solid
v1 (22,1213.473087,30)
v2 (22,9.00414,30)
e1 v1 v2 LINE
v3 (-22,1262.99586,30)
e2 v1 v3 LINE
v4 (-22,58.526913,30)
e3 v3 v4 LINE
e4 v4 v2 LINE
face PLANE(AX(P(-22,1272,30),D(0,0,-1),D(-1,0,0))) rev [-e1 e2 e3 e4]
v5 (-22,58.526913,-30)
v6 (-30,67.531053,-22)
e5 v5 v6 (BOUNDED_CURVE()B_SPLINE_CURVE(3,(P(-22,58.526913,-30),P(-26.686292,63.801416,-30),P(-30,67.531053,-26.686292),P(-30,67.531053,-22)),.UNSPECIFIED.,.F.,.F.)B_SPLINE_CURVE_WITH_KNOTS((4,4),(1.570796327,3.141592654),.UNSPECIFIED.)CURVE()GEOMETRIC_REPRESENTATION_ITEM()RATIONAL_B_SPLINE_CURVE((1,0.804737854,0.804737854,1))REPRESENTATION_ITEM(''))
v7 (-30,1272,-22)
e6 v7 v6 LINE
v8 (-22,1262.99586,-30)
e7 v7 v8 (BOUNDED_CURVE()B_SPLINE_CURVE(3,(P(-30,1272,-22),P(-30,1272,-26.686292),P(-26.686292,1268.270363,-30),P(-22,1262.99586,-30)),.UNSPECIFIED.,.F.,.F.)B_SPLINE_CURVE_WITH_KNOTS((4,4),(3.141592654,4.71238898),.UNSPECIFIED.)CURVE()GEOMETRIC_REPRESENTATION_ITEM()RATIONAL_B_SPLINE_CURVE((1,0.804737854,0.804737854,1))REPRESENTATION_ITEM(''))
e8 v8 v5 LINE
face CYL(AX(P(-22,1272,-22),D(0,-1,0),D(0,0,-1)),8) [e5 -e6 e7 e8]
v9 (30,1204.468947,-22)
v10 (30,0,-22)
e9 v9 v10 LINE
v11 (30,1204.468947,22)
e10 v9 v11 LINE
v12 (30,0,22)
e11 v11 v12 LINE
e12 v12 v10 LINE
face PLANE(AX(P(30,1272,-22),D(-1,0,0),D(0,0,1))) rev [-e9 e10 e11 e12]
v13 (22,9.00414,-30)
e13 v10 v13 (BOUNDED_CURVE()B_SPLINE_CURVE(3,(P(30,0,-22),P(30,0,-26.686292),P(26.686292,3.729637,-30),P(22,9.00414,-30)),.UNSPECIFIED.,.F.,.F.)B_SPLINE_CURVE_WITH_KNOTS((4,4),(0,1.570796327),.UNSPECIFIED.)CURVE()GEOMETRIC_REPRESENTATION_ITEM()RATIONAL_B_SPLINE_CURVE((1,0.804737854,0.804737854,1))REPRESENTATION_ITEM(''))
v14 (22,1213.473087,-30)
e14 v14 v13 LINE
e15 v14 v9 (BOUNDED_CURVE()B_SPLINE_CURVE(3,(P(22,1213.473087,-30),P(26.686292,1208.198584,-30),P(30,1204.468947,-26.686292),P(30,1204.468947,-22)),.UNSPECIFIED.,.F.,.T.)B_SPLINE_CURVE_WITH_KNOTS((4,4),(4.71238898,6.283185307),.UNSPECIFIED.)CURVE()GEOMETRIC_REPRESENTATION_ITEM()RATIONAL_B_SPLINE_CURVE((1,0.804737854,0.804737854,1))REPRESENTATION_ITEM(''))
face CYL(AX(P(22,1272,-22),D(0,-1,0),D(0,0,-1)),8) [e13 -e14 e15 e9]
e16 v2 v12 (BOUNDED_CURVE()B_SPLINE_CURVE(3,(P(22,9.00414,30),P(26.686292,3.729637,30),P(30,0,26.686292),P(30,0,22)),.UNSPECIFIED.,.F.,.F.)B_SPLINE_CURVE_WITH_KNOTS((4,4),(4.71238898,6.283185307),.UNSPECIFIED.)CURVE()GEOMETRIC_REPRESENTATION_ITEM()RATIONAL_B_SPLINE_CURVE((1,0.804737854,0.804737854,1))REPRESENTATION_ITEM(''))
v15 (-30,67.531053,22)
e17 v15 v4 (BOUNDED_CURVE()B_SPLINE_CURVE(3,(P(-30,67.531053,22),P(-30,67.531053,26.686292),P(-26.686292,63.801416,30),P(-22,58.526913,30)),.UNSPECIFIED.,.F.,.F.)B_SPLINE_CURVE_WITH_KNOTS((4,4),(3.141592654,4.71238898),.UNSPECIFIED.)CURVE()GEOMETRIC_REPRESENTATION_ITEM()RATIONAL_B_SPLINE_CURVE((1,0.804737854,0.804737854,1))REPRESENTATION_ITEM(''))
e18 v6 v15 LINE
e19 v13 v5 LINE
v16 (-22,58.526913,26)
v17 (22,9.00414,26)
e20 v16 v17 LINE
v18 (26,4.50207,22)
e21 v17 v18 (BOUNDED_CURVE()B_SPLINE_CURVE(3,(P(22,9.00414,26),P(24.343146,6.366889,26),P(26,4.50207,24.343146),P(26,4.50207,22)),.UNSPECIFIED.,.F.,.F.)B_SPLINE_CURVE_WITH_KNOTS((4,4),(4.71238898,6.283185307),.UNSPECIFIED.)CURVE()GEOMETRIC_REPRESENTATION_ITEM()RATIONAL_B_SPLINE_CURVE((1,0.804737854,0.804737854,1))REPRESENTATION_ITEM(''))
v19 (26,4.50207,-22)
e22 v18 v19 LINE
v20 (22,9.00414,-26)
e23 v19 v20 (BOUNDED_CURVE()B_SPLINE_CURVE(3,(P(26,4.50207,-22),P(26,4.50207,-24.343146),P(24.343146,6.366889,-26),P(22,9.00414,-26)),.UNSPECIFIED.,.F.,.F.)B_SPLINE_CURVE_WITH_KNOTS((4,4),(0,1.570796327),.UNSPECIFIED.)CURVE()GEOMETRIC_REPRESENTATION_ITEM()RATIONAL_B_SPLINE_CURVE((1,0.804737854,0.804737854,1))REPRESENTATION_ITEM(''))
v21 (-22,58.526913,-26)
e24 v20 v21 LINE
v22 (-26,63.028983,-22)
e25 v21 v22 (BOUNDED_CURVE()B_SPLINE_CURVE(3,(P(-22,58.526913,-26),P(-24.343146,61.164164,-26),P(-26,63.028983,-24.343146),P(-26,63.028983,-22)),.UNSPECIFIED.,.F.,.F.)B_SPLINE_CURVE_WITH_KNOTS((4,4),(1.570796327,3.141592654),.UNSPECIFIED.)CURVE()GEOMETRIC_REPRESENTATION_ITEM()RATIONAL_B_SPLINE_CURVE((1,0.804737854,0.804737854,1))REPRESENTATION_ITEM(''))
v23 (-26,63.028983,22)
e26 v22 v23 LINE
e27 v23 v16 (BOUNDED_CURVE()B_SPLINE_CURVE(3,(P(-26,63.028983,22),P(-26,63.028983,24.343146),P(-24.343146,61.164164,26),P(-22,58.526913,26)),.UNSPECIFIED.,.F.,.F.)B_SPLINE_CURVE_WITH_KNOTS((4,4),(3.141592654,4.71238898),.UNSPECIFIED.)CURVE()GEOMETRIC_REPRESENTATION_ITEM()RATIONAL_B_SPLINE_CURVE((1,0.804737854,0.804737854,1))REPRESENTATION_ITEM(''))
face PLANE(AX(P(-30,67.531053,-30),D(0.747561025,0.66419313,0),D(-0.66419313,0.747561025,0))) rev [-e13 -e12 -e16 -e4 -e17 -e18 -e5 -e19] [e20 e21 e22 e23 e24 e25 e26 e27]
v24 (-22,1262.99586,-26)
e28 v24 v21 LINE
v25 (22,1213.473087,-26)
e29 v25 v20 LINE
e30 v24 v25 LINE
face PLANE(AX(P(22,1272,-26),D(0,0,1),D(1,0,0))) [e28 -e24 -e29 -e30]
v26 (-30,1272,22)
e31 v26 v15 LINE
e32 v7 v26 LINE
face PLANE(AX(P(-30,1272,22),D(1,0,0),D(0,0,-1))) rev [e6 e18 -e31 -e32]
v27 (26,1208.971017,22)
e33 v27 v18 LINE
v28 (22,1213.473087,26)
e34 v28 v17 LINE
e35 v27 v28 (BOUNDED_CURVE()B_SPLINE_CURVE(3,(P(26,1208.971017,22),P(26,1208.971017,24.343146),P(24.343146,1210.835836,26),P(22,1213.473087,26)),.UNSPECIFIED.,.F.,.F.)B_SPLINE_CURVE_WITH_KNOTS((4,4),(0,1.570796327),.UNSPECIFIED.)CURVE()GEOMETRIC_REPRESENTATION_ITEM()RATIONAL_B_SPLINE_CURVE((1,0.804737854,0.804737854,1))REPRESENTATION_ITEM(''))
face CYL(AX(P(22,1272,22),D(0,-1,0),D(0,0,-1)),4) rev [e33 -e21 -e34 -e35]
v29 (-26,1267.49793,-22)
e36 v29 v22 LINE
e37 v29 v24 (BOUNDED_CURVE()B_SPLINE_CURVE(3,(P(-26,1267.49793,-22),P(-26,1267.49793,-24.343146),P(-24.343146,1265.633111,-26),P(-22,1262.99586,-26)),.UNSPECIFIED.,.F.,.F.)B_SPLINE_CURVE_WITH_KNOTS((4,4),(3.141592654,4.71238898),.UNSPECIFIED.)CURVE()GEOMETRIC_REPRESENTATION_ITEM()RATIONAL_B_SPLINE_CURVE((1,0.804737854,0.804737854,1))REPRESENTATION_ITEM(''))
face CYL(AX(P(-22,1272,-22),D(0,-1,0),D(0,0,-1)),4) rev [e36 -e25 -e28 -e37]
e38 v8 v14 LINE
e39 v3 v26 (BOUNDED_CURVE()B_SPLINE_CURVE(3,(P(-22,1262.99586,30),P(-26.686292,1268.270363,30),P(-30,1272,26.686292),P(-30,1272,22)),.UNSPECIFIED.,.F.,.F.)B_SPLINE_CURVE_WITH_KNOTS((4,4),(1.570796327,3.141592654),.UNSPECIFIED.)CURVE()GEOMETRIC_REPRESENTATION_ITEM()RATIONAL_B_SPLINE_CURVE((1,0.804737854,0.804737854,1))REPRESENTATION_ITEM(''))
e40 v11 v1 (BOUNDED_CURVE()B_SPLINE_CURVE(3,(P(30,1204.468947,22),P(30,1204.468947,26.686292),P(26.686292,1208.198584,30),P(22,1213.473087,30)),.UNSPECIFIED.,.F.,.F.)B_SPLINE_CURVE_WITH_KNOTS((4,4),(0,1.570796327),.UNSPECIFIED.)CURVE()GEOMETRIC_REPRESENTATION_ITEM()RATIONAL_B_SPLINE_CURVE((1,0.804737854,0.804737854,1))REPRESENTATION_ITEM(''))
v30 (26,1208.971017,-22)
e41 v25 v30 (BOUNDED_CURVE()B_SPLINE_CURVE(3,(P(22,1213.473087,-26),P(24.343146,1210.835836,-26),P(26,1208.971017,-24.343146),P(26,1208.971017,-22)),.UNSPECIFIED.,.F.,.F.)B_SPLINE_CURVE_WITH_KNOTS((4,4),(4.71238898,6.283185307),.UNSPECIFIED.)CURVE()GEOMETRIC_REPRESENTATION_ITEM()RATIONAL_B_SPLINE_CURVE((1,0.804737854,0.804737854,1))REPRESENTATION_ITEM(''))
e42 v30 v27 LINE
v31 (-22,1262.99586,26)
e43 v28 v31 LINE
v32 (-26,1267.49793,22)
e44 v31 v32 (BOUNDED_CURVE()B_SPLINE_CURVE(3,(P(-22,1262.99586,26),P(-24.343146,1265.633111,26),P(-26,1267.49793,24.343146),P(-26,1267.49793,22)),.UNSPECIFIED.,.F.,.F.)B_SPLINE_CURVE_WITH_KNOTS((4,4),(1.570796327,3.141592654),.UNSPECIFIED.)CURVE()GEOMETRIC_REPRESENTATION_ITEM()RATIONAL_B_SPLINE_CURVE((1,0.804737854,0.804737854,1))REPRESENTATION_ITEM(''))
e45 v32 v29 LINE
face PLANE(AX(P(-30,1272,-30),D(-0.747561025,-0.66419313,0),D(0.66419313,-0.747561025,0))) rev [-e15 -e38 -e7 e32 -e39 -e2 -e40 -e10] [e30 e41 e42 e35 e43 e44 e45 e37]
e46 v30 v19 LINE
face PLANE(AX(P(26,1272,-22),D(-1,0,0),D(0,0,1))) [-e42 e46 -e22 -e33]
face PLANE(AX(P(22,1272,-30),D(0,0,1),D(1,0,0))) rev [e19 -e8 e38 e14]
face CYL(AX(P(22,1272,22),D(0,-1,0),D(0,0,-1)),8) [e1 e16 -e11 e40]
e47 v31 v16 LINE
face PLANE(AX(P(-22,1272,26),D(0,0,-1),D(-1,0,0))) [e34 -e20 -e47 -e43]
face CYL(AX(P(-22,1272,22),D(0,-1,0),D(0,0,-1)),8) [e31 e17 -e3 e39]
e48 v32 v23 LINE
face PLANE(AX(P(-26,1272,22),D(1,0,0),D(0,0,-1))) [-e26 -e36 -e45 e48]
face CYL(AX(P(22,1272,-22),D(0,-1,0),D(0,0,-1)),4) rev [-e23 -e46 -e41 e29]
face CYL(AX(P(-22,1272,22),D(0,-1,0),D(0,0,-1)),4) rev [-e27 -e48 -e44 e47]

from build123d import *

# Parameters (mm, degrees)
GB_T_6728_2002_SQUARE_HOLLOW_SECTION_60_DEPTH = 1272
CUT_EXTRUDE1_DEPTH                            = 1274.767639721
CUT_EXTRUDE1_DEPTH_BACK                       = 1274.767639721


with BuildPart() as part:
    # Sketch1 → GB/T 6728-2002 square hollow section 60×60×4(1) (new body)
    with BuildSketch(Plane(origin=(0, 0, 0), x_dir=(-1, 0, 0), z_dir=(0, 1, 0))):
        with BuildLine():
            Line((-22, -30), (22, -30))
            ThreePointArc((22, -30), (27.656854249, -27.656854249), (30, -22))
            Line((30, -22), (30, 22))
            ThreePointArc((30, 22), (27.656854249, 27.656854249), (22, 30))
            Line((22, 30), (-22, 30))
            ThreePointArc((-22, 30), (-27.656854249, 27.656854249), (-30, 22))
            Line((-30, 22), (-30, -22))
            ThreePointArc((-30, -22), (-27.656854249, -27.656854249), (-22, -30))
        make_face()
        with BuildLine():
            Line((-22, -26), (22, -26))
            ThreePointArc((22, -26), (24.828427125, -24.828427125), (26, -22))
            Line((26, -22), (26, 22))
            ThreePointArc((26, 22), (24.828427125, 24.828427125), (22, 26))
            Line((22, 26), (-22, 26))
            ThreePointArc((-22, 26), (-24.828427125, 24.828427125), (-26, 22))
            Line((-26, 22), (-26, -22))
            ThreePointArc((-26, -22), (-24.828427125, -24.828427125), (-22, -26))
        make_face(mode=Mode.SUBTRACT)
    extrude(amount=GB_T_6728_2002_SQUARE_HOLLOW_SECTION_60_DEPTH)

    # Sketch2 → Cut-Extrude1 (cut, two sides: drawn at the far end of the back side and taken through both)
    with BuildSketch(Plane.XY.offset(30).offset(-CUT_EXTRUDE1_DEPTH_BACK)):
        Polygon((-30, 1272), (30, 1204.468946968), (30, 1272), align=None)
        Polygon((-30, 0), (-30, 67.531053032), (30, 0), align=None)
    extrude(amount=CUT_EXTRUDE1_DEPTH + CUT_EXTRUDE1_DEPTH_BACK, mode=Mode.SUBTRACT)


solid = part.part
